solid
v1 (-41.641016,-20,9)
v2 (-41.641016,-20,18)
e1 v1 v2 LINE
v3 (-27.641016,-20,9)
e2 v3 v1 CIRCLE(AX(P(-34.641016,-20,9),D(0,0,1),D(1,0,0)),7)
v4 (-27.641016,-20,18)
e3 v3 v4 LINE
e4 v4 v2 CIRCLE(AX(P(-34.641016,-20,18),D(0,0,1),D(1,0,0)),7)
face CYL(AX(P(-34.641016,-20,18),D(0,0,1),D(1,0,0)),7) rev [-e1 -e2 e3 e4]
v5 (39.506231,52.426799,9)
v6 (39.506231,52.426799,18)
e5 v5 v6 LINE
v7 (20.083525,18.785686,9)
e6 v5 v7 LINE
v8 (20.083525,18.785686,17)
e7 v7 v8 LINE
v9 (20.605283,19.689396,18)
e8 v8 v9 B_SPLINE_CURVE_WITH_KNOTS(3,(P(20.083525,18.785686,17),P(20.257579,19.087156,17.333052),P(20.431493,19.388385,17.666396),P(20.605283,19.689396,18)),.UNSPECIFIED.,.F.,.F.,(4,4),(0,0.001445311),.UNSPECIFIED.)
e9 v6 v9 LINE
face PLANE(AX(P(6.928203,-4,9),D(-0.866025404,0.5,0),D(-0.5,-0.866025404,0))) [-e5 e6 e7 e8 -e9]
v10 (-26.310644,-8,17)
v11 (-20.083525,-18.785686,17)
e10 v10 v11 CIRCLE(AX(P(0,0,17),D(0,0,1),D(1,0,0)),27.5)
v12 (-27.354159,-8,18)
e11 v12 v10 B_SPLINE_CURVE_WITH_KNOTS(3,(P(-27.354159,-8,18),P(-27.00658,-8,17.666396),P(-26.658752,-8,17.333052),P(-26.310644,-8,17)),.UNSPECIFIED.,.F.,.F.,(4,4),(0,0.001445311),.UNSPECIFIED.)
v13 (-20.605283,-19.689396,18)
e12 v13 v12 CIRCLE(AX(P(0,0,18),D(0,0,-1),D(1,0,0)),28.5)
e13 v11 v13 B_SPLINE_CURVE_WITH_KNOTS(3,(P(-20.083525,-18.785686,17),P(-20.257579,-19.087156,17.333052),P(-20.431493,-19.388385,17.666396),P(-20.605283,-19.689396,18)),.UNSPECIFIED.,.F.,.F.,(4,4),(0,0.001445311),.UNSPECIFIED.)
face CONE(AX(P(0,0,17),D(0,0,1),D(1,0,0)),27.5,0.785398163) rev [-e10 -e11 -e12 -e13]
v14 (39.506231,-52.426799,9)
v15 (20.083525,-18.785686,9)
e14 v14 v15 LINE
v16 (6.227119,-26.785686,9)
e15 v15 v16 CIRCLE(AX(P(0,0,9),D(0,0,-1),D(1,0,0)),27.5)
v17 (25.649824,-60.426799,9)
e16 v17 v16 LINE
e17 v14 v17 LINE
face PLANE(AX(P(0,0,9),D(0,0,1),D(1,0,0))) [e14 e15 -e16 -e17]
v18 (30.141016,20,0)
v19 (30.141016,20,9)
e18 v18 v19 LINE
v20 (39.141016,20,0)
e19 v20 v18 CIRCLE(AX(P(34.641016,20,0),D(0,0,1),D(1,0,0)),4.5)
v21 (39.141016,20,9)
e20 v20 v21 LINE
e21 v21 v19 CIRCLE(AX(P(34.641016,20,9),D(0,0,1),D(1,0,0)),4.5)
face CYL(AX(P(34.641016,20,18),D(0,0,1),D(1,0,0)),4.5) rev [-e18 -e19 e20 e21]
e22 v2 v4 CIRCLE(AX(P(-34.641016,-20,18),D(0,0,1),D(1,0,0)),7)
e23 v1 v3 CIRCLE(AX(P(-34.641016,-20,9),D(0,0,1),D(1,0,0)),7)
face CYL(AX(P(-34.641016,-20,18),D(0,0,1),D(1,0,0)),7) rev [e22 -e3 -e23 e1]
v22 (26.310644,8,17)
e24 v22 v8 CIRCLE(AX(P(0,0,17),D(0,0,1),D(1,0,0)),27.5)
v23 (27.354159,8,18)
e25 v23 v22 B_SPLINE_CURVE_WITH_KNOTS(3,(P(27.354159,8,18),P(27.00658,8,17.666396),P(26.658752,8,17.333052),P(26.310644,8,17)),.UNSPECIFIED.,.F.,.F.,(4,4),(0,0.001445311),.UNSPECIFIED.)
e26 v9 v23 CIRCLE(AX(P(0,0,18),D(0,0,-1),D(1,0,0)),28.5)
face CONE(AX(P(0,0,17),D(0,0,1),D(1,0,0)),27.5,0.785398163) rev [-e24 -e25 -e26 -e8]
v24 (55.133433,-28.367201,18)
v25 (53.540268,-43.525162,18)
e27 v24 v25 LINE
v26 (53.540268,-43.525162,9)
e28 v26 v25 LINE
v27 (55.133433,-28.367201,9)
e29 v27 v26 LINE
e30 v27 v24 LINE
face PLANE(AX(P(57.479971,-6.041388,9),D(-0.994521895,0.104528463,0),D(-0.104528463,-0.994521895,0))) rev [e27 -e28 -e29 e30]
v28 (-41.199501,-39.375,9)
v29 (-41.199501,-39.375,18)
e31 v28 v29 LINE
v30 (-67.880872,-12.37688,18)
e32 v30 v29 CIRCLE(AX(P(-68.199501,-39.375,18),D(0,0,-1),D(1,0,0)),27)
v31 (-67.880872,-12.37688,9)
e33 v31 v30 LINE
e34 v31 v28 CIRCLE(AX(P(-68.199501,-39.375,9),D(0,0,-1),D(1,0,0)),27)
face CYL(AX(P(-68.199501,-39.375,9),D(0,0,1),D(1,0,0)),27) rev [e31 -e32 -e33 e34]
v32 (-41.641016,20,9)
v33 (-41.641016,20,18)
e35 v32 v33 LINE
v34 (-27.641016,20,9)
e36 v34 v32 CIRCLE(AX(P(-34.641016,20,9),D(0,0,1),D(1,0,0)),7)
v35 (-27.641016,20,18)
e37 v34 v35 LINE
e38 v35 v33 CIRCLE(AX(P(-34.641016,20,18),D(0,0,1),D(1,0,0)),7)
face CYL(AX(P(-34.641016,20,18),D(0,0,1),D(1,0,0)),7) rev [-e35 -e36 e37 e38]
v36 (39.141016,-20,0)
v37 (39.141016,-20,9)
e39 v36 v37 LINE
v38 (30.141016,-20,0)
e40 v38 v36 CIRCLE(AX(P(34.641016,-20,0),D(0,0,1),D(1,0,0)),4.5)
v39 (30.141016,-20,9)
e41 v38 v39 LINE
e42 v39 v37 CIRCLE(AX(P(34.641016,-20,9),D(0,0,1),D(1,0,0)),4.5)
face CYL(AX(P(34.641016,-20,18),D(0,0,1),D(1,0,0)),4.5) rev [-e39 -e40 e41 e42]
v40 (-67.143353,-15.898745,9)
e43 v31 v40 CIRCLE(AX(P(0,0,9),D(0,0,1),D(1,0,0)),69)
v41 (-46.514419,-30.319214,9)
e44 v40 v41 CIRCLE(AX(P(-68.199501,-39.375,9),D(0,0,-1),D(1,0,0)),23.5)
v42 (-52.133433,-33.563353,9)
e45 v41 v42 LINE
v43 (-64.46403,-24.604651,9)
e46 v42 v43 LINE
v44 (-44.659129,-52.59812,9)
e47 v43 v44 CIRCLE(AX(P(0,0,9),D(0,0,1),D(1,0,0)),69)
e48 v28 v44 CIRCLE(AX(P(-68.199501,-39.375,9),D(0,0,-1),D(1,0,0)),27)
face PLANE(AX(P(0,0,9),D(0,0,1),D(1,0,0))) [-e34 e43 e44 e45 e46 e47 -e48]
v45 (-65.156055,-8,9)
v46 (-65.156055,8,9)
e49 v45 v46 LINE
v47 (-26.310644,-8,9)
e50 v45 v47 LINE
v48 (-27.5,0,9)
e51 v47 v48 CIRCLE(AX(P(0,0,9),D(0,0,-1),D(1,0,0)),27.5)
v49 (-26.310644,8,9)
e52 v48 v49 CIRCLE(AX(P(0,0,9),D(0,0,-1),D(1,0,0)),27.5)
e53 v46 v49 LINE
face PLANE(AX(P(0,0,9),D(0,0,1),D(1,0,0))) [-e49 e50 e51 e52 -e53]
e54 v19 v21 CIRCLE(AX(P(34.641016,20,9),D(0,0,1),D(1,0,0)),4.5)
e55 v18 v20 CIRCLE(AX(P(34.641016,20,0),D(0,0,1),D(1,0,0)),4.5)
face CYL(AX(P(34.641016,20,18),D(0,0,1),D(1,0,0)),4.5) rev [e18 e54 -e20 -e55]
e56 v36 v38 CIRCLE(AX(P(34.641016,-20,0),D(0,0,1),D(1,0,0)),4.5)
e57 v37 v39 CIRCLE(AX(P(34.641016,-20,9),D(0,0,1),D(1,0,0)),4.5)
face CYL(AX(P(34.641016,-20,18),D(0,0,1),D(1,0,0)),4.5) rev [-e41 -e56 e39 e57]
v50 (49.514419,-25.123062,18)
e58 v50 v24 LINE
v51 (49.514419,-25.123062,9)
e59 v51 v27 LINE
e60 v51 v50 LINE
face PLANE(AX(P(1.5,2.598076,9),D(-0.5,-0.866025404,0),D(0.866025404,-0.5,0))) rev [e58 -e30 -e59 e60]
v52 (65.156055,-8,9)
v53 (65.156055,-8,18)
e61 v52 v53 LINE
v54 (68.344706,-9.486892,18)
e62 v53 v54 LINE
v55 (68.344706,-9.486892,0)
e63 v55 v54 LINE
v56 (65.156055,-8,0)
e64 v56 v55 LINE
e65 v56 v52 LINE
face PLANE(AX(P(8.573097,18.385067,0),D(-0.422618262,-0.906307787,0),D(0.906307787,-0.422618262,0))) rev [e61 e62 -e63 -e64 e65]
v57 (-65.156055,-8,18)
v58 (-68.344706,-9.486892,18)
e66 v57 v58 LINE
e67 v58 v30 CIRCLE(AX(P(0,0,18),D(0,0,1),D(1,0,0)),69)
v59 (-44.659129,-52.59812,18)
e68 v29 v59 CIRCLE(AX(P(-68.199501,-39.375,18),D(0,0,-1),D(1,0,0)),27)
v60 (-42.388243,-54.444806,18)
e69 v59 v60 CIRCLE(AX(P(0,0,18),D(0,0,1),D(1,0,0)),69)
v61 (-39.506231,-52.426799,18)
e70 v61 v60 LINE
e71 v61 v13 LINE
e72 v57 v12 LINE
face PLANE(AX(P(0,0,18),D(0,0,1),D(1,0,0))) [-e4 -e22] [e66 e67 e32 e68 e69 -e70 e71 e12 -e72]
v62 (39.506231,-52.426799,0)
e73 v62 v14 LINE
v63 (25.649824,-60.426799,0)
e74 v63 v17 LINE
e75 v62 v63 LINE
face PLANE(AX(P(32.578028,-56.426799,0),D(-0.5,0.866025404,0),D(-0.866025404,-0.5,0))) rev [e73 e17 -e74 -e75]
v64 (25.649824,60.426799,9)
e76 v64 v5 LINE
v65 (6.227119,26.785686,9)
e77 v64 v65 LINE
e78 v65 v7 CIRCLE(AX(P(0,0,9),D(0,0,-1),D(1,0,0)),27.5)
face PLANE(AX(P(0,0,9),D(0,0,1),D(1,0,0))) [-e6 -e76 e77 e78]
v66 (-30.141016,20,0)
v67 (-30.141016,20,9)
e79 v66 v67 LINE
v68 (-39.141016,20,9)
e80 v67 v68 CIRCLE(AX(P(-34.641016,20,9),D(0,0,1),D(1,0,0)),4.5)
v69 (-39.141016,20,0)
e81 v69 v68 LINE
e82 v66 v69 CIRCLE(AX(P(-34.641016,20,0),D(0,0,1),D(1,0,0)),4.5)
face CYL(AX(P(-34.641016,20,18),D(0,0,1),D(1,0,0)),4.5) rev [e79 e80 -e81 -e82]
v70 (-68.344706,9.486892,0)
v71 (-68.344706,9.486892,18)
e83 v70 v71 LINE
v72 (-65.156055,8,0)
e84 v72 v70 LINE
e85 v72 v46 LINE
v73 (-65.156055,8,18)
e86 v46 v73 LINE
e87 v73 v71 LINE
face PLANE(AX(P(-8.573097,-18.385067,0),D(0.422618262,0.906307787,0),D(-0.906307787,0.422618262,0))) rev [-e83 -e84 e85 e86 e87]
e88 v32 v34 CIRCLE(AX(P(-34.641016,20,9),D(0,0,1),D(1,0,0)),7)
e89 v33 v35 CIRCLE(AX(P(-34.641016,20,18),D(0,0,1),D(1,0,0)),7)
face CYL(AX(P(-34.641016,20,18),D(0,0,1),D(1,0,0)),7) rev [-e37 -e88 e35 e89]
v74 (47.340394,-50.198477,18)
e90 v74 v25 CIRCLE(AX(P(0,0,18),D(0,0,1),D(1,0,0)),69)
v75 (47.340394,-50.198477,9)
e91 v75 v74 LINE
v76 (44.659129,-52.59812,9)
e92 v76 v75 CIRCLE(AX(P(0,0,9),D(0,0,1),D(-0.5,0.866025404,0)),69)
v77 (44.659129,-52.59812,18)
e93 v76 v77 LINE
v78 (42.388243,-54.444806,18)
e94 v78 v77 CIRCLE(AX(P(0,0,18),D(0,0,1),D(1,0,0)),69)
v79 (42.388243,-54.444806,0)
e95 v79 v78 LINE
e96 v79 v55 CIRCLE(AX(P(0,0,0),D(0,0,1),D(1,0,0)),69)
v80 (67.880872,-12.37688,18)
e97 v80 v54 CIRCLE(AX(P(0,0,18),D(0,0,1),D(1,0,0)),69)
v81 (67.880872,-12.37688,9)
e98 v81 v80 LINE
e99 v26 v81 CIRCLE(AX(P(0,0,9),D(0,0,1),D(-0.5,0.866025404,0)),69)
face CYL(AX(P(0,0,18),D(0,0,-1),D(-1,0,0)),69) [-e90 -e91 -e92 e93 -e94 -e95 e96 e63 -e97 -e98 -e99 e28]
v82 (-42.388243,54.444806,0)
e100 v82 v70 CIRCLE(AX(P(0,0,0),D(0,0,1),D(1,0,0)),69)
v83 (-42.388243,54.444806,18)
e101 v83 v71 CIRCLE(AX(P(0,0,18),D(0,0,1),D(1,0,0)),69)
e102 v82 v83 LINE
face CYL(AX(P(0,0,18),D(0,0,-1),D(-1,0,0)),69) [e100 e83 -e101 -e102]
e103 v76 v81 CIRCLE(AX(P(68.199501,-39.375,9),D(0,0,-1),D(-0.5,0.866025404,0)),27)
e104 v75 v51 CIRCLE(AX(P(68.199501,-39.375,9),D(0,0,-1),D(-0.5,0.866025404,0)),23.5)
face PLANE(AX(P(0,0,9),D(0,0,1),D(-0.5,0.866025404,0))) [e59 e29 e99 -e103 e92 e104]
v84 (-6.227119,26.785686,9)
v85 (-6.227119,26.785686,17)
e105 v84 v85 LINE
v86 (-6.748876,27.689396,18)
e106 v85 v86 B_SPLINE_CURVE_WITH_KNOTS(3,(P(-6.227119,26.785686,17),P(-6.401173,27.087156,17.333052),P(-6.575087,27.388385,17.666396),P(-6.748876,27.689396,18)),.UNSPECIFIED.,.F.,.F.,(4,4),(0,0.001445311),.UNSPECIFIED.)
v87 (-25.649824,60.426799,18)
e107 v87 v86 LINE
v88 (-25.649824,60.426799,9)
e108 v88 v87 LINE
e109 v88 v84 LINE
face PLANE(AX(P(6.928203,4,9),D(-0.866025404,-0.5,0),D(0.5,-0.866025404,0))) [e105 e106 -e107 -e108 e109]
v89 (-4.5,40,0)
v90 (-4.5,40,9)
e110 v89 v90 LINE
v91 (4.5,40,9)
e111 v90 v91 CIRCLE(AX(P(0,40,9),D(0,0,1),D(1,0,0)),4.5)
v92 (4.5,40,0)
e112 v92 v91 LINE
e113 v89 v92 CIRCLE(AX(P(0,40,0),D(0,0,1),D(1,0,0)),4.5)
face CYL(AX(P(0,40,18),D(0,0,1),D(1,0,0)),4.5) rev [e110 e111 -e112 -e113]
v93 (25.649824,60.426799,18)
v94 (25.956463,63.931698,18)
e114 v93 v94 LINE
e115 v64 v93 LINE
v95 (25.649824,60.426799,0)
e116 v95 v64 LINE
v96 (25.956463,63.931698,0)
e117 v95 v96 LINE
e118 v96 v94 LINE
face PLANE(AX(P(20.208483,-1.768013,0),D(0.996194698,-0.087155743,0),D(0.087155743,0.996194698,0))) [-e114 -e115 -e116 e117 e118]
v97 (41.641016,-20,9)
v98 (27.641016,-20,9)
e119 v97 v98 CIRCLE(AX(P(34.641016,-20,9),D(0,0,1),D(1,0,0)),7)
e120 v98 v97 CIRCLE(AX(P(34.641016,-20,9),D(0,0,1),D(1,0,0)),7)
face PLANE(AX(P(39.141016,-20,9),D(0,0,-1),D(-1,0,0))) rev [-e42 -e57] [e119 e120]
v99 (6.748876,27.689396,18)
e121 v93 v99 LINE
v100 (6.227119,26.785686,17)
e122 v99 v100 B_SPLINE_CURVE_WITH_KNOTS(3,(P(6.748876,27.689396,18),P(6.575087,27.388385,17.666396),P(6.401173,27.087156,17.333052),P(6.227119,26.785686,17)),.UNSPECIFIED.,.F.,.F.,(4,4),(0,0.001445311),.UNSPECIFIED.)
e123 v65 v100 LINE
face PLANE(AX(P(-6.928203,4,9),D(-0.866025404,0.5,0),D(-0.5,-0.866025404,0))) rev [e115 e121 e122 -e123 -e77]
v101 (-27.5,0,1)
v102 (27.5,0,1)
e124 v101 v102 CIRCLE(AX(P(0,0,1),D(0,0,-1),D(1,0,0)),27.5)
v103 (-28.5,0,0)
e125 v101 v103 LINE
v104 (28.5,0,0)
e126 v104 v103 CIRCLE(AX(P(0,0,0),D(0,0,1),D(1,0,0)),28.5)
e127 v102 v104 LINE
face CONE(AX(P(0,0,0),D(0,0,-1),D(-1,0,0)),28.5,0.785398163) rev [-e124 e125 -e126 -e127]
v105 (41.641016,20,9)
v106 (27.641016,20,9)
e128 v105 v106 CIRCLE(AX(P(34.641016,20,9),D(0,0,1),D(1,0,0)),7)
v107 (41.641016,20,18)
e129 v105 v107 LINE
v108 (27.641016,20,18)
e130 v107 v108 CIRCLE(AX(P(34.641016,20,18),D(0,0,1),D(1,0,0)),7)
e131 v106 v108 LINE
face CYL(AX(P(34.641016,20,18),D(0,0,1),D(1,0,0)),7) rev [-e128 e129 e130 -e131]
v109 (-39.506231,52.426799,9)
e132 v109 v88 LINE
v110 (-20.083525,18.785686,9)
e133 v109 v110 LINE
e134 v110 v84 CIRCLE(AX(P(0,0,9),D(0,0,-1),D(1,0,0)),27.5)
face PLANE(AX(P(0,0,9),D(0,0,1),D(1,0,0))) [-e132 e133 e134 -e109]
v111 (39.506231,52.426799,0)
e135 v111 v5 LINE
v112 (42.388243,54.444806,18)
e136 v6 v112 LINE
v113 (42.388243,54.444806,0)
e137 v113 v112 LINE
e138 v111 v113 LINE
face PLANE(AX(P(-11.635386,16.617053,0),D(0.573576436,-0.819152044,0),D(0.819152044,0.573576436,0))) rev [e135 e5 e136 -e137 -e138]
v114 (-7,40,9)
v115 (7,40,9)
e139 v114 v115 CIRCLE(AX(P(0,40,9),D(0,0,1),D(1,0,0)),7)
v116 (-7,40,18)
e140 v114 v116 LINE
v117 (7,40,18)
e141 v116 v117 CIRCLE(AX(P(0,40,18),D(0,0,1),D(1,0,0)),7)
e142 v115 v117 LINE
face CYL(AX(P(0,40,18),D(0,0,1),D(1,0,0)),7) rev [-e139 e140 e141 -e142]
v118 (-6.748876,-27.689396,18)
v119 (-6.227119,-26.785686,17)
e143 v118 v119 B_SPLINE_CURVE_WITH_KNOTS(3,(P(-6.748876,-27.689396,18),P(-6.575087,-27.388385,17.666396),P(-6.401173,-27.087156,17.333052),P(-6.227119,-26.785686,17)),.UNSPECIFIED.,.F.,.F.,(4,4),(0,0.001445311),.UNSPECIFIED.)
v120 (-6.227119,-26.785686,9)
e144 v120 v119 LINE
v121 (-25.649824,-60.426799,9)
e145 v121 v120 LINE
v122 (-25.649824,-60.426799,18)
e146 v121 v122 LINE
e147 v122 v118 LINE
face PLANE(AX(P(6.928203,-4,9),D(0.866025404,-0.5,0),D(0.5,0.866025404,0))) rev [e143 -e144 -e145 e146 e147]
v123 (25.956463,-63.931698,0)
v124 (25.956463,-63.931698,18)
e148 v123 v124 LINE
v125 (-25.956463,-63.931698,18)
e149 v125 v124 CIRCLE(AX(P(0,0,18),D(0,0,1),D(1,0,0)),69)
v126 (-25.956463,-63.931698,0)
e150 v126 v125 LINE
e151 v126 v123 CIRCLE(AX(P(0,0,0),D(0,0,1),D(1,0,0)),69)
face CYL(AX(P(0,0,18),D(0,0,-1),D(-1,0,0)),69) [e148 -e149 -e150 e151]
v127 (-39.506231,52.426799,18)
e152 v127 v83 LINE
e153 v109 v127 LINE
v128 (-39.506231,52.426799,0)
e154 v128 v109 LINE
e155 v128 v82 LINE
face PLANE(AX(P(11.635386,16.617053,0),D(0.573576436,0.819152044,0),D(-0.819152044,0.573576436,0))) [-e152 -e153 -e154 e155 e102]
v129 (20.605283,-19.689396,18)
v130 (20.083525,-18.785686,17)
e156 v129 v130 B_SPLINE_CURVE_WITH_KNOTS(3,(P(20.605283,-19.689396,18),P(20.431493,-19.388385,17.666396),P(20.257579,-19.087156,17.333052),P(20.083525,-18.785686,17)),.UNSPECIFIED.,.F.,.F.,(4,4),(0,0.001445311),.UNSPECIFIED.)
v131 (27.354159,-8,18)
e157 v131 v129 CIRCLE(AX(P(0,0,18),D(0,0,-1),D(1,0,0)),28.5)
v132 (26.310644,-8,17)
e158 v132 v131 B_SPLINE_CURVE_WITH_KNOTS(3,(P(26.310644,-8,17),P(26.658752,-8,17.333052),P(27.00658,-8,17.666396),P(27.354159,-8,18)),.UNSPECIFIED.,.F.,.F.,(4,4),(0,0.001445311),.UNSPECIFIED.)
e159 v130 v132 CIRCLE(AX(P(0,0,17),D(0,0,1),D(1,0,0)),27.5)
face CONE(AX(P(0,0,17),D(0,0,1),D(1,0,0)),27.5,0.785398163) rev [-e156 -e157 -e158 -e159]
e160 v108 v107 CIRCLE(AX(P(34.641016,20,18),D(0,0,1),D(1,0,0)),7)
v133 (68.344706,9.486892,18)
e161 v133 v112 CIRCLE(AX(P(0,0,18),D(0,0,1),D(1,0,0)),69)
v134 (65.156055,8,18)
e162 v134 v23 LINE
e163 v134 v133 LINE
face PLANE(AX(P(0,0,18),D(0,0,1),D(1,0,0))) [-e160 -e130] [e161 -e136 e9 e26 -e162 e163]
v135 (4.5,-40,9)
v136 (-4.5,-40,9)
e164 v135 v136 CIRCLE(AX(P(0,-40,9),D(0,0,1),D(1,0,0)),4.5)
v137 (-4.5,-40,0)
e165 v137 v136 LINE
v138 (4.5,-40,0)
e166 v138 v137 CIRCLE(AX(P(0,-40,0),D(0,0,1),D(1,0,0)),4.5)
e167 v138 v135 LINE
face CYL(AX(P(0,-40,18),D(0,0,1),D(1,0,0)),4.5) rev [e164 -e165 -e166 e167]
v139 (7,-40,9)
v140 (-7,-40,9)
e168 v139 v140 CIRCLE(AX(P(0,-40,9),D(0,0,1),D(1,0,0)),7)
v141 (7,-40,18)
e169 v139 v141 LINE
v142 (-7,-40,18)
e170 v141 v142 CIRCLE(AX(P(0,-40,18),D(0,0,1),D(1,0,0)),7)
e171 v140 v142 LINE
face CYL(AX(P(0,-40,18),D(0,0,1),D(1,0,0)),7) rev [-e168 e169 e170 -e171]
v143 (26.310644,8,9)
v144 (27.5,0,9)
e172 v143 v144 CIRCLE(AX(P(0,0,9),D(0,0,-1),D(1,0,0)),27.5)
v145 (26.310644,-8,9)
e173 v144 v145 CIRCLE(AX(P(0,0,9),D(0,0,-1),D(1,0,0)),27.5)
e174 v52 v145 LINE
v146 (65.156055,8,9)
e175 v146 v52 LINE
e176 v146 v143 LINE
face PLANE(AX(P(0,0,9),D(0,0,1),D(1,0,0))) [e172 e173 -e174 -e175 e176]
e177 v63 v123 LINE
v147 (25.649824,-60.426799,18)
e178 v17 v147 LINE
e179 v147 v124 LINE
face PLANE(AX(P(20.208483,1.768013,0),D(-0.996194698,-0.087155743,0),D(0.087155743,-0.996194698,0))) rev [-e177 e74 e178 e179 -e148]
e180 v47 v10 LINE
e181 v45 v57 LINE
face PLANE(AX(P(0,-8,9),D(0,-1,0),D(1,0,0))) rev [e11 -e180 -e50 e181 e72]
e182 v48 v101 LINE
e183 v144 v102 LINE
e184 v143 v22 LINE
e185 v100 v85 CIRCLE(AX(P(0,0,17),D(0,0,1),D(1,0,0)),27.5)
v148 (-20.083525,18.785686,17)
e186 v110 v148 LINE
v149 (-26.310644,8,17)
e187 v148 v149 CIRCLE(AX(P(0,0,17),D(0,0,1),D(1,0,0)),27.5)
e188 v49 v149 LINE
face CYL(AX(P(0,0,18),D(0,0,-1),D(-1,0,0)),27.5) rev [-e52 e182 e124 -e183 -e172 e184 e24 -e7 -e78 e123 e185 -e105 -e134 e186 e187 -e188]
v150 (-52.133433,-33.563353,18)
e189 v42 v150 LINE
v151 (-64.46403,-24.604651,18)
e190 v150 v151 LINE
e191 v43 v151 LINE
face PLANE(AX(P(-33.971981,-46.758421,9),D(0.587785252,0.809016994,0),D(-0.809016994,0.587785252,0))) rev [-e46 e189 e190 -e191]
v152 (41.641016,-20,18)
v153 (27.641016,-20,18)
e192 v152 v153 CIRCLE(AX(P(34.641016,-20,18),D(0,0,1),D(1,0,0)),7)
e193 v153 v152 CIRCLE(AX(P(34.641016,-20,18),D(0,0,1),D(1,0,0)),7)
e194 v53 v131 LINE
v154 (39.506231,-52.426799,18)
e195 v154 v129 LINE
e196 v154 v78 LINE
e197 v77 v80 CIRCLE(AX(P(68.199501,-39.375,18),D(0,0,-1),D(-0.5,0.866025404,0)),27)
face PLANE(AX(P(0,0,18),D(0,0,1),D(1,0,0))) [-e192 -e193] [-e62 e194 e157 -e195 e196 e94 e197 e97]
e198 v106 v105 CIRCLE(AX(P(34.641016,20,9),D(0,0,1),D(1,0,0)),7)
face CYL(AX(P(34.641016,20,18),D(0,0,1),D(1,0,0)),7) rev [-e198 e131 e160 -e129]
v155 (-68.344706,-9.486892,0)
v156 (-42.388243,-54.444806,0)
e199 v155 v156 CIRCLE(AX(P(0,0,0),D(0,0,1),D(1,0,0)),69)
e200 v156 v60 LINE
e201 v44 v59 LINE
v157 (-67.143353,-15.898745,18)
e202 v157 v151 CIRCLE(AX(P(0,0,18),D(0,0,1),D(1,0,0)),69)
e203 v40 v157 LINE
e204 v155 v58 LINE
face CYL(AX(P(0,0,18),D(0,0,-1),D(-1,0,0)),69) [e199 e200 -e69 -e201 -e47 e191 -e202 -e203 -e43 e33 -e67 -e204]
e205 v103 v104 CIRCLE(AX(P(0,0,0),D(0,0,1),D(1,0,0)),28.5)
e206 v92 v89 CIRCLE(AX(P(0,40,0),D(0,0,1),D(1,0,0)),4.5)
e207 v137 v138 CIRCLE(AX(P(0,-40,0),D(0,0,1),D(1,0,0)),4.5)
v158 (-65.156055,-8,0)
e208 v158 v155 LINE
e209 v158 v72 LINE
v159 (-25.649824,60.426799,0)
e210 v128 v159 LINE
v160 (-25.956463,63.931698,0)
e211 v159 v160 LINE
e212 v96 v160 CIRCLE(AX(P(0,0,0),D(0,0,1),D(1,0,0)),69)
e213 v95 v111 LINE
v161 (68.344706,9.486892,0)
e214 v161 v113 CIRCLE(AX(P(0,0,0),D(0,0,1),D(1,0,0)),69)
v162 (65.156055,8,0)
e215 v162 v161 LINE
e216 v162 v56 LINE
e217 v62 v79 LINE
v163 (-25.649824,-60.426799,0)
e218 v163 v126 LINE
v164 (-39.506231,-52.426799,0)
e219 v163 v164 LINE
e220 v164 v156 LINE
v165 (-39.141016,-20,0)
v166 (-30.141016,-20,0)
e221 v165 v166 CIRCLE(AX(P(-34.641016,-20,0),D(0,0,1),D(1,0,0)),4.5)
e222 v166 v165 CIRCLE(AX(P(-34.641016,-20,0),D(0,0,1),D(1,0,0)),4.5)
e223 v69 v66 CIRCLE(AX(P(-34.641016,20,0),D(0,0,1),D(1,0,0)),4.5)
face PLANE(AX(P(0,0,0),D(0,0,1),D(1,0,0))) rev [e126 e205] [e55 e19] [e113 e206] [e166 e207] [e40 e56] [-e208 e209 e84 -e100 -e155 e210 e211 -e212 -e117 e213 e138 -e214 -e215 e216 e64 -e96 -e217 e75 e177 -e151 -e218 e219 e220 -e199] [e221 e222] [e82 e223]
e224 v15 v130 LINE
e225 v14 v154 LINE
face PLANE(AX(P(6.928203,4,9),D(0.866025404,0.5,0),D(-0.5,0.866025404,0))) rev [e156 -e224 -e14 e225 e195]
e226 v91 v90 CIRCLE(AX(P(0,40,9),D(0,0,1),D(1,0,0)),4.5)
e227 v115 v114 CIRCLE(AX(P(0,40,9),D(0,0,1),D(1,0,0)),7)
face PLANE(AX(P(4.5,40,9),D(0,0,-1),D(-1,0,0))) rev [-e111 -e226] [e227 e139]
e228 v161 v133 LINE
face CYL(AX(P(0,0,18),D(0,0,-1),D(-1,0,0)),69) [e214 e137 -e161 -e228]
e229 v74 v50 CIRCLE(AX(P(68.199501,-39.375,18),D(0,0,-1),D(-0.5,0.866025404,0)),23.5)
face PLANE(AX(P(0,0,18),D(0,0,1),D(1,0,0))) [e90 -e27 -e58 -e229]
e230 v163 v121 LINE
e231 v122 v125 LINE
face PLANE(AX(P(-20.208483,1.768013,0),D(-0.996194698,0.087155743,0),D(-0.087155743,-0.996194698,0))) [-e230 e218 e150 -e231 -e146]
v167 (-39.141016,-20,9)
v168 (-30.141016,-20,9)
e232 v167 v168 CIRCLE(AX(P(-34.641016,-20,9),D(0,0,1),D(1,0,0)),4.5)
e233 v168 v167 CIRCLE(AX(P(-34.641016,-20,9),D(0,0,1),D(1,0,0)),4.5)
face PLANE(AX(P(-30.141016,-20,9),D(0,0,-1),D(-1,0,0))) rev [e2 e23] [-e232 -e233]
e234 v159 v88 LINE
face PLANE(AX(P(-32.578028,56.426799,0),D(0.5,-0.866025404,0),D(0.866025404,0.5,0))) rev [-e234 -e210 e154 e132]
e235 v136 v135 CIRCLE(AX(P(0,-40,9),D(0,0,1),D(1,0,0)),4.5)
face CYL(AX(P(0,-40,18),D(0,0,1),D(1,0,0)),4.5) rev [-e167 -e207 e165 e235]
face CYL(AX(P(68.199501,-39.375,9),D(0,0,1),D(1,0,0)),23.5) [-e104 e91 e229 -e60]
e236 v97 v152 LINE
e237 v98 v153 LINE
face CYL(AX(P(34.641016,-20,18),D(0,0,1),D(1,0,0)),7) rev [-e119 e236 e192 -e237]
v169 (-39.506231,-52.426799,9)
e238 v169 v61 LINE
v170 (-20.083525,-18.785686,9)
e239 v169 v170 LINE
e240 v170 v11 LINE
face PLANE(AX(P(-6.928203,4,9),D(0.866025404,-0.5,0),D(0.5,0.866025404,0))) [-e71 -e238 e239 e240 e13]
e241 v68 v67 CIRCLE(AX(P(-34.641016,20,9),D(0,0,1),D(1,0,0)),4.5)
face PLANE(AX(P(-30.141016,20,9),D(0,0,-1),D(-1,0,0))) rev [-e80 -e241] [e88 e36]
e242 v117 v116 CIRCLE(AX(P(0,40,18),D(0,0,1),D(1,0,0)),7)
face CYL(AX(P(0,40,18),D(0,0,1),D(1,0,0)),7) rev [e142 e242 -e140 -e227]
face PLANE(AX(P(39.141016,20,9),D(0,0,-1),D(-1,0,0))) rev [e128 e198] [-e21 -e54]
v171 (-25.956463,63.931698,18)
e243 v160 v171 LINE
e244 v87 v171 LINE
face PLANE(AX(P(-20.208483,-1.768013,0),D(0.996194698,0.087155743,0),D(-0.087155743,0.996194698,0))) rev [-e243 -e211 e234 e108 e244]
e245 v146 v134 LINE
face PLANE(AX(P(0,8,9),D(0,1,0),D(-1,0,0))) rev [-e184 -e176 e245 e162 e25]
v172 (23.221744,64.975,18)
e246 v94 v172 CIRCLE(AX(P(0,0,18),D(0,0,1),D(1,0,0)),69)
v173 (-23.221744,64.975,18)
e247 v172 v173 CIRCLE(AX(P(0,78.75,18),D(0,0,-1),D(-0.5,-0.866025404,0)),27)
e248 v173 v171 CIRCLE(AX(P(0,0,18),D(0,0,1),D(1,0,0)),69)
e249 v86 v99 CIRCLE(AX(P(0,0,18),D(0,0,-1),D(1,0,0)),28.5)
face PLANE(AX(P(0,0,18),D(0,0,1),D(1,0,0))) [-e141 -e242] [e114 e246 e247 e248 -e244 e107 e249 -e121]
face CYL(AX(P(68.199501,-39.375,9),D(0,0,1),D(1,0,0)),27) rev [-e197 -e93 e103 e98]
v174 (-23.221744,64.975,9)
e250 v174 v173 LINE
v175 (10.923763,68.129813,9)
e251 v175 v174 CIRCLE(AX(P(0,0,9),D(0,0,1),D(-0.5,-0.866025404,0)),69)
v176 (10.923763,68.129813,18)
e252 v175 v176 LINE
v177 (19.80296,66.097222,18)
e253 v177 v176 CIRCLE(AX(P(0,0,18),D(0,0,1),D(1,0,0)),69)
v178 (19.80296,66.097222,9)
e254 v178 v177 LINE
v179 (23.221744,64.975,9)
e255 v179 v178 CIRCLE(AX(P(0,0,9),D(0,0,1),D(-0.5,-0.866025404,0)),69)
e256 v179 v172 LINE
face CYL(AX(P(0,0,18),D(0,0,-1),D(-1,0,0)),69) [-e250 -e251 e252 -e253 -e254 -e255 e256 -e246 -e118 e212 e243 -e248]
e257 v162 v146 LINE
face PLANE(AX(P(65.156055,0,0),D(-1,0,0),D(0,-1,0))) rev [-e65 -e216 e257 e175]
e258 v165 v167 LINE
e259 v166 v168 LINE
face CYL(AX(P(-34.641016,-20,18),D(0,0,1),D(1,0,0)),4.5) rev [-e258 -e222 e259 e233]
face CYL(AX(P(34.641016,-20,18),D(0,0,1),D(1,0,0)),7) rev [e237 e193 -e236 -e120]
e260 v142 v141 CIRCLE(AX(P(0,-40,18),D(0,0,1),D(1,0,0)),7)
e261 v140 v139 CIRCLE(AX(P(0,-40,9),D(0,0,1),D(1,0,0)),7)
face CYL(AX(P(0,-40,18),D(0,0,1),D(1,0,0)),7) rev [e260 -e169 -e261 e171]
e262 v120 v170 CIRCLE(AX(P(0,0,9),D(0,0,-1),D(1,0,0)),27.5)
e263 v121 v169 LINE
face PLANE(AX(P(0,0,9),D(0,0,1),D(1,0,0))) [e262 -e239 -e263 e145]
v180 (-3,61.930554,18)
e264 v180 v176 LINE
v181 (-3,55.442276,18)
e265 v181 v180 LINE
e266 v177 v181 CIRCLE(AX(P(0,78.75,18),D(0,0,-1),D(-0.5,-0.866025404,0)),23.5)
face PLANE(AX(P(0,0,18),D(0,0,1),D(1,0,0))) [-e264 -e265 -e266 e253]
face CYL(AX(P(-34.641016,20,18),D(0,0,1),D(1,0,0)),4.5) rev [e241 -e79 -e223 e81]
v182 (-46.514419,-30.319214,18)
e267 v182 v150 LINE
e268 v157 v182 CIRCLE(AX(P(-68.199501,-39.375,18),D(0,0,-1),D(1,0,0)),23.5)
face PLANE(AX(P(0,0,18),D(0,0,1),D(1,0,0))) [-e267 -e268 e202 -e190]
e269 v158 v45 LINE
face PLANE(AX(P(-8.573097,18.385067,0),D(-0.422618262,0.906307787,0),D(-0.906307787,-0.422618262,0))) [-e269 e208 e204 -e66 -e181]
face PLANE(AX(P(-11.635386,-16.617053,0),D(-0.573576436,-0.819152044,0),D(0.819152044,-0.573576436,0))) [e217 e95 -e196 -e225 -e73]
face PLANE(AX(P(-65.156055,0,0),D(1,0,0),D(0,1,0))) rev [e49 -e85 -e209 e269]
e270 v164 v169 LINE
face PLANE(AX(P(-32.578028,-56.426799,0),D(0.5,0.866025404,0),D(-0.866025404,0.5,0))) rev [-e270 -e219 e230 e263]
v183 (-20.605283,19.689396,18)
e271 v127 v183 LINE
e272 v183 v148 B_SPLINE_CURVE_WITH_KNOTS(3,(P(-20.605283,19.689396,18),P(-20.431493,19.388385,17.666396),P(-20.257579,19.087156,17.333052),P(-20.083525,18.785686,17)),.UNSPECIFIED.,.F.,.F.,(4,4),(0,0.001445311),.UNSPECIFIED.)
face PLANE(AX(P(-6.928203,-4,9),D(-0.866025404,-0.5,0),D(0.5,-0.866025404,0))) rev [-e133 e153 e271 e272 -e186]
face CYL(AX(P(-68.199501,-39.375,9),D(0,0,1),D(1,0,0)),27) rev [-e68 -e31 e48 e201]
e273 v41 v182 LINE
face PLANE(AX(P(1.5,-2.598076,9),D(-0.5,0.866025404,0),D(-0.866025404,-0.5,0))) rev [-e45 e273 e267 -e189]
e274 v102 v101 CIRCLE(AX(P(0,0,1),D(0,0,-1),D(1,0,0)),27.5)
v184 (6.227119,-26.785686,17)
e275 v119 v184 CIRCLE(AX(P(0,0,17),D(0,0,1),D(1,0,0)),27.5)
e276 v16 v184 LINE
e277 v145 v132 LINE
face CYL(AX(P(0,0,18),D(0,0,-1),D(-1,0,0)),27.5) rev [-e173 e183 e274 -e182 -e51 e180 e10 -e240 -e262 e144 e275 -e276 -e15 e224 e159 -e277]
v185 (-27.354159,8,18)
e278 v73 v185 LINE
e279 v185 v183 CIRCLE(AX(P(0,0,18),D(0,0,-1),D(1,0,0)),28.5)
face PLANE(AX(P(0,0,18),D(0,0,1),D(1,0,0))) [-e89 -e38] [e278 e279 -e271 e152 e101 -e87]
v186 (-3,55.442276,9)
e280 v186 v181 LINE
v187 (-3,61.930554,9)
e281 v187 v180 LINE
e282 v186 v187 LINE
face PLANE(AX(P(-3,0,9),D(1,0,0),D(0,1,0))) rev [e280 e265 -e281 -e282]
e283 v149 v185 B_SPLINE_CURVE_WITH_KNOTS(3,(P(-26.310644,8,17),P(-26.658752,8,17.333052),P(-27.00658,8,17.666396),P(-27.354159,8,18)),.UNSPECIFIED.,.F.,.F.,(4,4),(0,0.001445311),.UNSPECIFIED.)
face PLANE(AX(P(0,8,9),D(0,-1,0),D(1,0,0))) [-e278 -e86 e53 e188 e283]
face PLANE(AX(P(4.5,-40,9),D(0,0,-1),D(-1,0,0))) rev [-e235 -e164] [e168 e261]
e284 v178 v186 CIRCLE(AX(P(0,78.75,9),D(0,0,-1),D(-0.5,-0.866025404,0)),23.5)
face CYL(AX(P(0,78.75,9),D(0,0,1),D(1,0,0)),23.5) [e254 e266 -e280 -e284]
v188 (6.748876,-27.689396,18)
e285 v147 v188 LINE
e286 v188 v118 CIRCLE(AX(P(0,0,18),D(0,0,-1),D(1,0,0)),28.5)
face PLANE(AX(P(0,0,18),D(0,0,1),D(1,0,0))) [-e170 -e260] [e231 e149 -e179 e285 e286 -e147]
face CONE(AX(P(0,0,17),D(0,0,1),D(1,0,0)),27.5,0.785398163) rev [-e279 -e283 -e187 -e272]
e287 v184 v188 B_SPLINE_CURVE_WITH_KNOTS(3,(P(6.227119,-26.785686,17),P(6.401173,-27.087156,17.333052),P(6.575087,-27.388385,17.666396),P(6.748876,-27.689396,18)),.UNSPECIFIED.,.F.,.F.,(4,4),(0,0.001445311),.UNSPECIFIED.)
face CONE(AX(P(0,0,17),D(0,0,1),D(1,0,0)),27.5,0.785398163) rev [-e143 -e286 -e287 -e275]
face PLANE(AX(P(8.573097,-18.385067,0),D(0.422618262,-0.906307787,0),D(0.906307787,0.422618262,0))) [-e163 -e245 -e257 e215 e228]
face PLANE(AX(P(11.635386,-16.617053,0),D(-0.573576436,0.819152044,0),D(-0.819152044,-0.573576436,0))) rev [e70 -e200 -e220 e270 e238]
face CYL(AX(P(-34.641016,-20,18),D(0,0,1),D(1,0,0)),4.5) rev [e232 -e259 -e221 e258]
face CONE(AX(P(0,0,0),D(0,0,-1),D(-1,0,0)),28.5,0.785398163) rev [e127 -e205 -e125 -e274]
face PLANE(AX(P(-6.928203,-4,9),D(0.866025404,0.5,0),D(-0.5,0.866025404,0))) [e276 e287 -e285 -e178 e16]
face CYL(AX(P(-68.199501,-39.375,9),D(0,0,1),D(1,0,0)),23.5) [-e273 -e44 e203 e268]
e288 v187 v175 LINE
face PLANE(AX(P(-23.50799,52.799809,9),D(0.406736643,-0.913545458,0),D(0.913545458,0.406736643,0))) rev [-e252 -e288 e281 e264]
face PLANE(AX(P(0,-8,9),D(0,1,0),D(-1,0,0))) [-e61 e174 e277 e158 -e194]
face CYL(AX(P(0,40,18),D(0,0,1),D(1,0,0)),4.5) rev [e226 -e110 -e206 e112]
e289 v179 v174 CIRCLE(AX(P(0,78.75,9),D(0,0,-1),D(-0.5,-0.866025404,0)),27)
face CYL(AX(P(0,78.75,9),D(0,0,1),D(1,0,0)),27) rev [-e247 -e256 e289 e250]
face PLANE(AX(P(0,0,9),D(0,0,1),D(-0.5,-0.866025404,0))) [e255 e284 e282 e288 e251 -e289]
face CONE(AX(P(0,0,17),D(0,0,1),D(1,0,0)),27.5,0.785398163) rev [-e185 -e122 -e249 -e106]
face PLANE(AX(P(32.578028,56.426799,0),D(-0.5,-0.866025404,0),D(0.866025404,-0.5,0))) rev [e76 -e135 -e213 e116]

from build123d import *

# Parameters (mm, degrees)
FLANGE_DISC_SKETCH_R                = 69
FLANGE_DISC_SKETCH_R_2              = 27.5
FLANGE_DISC_138_X_18_DEPTH          = 18
JAW_START                           = -9
JAW_RECESSES_9_DEEP_DEPTH           = 9
PORT_PROFILE_CUT_DEPTH              = 100.227012451
COUNTERBORED_HOLES_6X_9_D           = 9
COUNTERBORED_HOLES_6X_9_CBORE_D     = 14
COUNTERBORED_HOLES_6X_9_CBORE_DEPTH = 9
HOOK_START                          = -9
HOOK_SLOT_9_DEEP_DEPTH              = 9
HOOK_SLOT_PATTERN_3X_COUNT          = 3
EDGE_CHAMFER_1X45_SIZE              = 1


with BuildPart() as part:
    # Flange Disc Sketch → Flange Disc _138 x 18 (new body)
    with BuildSketch(Plane.XY):
        Circle(FLANGE_DISC_SKETCH_R)
        Circle(FLANGE_DISC_SKETCH_R_2, mode=Mode.SUBTRACT)
    extrude(amount=FLANGE_DISC_138_X_18_DEPTH)

    # Jaw And Port Sketch → Jaw Recesses 9 Deep (cut)
    with BuildSketch(Plane.XY.offset(18).offset(JAW_START)):
        with BuildLine():
            ThreePointArc((-26.310644234, -8), (-27.5, 0), (-26.310644234, 8))
            Line((-26.310644234, 8), (-65.156055364, 8))
            Line((-65.156055364, 8), (-65.156055364, -8))
            Line((-65.156055364, -8), (-26.310644234, -8))
        make_face()
        with BuildLine():
            Line((-6.227118887, 26.785686296), (-25.649824452, 60.426799156))
            Line((-25.649824452, 60.426799156), (-39.506230912, 52.426799156))
            Line((-39.506230912, 52.426799156), (-20.083525347, 18.785686296))
            ThreePointArc((-20.083525347, 18.785686296), (-13.75, 23.815698604), (-6.227118887, 26.785686296))
        make_face()
        with BuildLine():
            Line((25.649824452, 60.426799156), (6.227118887, 26.785686296))
            ThreePointArc((6.227118887, 26.785686296), (13.75, 23.815698604), (20.083525347, 18.785686296))
            Line((20.083525347, 18.785686296), (39.506230912, 52.426799156))
            Line((39.506230912, 52.426799156), (25.649824452, 60.426799156))
        make_face()
        with BuildLine():
            Line((65.156055364, 8), (26.310644234, 8))
            ThreePointArc((26.310644234, 8), (27.201035977, 4.043963623), (27.5, 0))
            ThreePointArc((27.5, 0), (27.201035977, -4.043963623), (26.310644234, -8))
            Line((26.310644234, -8), (65.156055364, -8))
            Line((65.156055364, -8), (65.156055364, 8))
        make_face()
        with BuildLine():
            Line((39.506230912, -52.426799156), (20.083525347, -18.785686296))
            ThreePointArc((20.083525347, -18.785686296), (13.75, -23.815698604), (6.227118887, -26.785686296))
            Line((6.227118887, -26.785686296), (25.649824452, -60.426799156))
            Line((25.649824452, -60.426799156), (39.506230912, -52.426799156))
        make_face()
        with BuildLine():
            ThreePointArc((-6.227118887, -26.785686296), (-13.75, -23.815698604), (-20.083525347, -18.785686296))
            Line((-20.083525347, -18.785686296), (-39.506230912, -52.426799156))
            Line((-39.506230912, -52.426799156), (-25.649824452, -60.426799156))
            Line((-25.649824452, -60.426799156), (-6.227118887, -26.785686296))
        make_face()
    extrude(amount=JAW_RECESSES_9_DEEP_DEPTH, mode=Mode.SUBTRACT)

    # Sketch3_3 → Port Profile Cut (cut, through all)
    with BuildSketch(Plane.XY.offset(18)):
        with BuildLine():
            Line((-65.156055364, 8), (-68.344706261, 9.486892332))
            ThreePointArc((-68.344706261, 9.486892332), (-69, 0), (-68.344706261, -9.486892332))
            Line((-68.344706261, -9.486892332), (-65.156055364, -8))
            Line((-65.156055364, -8), (-65.156055364, 8))
        make_face()
        with BuildLine():
            Line((-39.506230912, -52.426799156), (-42.388242893, -54.44480567))
            ThreePointArc((-42.388242893, -54.44480567), (-34.5, -59.755752861), (-25.956463368, -63.931698002))
            Line((-25.956463368, -63.931698002), (-25.649824452, -60.426799156))
            Line((-25.649824452, -60.426799156), (-39.506230912, -52.426799156))
        make_face()
        with BuildLine():
            ThreePointArc((25.956463368, -63.931698002), (34.5, -59.755752861), (42.388242893, -54.44480567))
            Line((42.388242893, -54.44480567), (39.506230912, -52.426799156))
            Line((39.506230912, -52.426799156), (25.649824452, -60.426799156))
            Line((25.649824452, -60.426799156), (25.956463368, -63.931698002))
        make_face()
        with BuildLine():
            ThreePointArc((69, 0), (68.835981623, 4.754748574), (68.344706261, 9.486892332))
            Line((68.344706261, 9.486892332), (65.156055364, 8))
            Line((65.156055364, 8), (65.156055364, -8))
            Line((65.156055364, -8), (68.344706261, -9.486892332))
            ThreePointArc((68.344706261, -9.486892332), (68.835981623, -4.754748574), (69, 0))
        make_face()
        with BuildLine():
            ThreePointArc((42.388242893, 54.44480567), (34.5, 59.755752861), (25.956463368, 63.931698002))
            Line((25.956463368, 63.931698002), (25.649824452, 60.426799156))
            Line((25.649824452, 60.426799156), (39.506230912, 52.426799156))
            Line((39.506230912, 52.426799156), (42.388242893, 54.44480567))
        make_face()
        with BuildLine():
            Line((-39.506230912, 52.426799156), (-25.649824452, 60.426799156))
            Line((-25.649824452, 60.426799156), (-25.956463368, 63.931698002))
            ThreePointArc((-25.956463368, 63.931698002), (-34.5, 59.755752861), (-42.388242893, 54.44480567))
            Line((-42.388242893, 54.44480567), (-39.506230912, 52.426799156))
        make_face()
    extrude(amount=-PORT_PROFILE_CUT_DEPTH, mode=Mode.SUBTRACT)

    # Counterbored Holes 6x_9 (through all)
    with Locations(Plane.XY.offset(18)):
        with Locations((0, 40), (34.641016151, 20), (34.641016151, -20), (0, -40), (-34.641016151, -20), (-34.641016151, 20)):
            CounterBoreHole(COUNTERBORED_HOLES_6X_9_D / 2, COUNTERBORED_HOLES_6X_9_CBORE_D / 2, COUNTERBORED_HOLES_6X_9_CBORE_DEPTH)

    # Hook Slot Sketch → Hook Slot 9 Deep (cut)
    with BuildSketch(Plane.XY.offset(18).offset(HOOK_START)):
        with BuildLine():
            ThreePointArc((-67.143353435, -15.898744905), (-54.735535714, -20.114375634), (-46.514419424, -30.319214191))
            Line((-46.514419424, -30.319214191), (-52.133433448, -33.56335345))
            Line((-52.133433448, -33.56335345), (-64.464030022, -24.604650643))
            ThreePointArc((-64.464030022, -24.604650643), (-56.328274682, -39.851291966), (-44.65912882, -52.598119862))
            ThreePointArc((-44.65912882, -52.598119862), (-44.816814646, -25.875), (-67.880872402, -12.376880138))
            ThreePointArc((-67.880872402, -12.376880138), (-67.535074395, -14.142620919), (-67.143353435, -15.898744905))
        make_face()
    hook_slot_9_deep = extrude(amount=HOOK_SLOT_9_DEEP_DEPTH, mode=Mode.SUBTRACT)

    # Hook Slot Pattern 3x: Hook Slot 9 Deep ×3 about axis
    hook_slot_pattern_3x_axis = Axis((0, 0, 0), (0, 0, 1))
    for i in range(1, HOOK_SLOT_PATTERN_3X_COUNT):
        add(hook_slot_9_deep.rotate(hook_slot_pattern_3x_axis, i * 360 / HOOK_SLOT_PATTERN_3X_COUNT), mode=Mode.SUBTRACT)

    # Edge Chamfer 1x45
    edge_chamfer_1x45_edges = [part.edges().sort_by_distance(p)[0] for p in [
        (0, 27.5, 18),
        (-23.815698604, 13.75, 18),
        (-23.815698604, -13.75, 18),
        (0, -27.5, 18),
        (23.815698604, -13.75, 18),
        (-27.5, 0, 0),
        (23.815698604, 13.75, 18),
    ]]
    chamfer(edge_chamfer_1x45_edges, length=EDGE_CHAMFER_1X45_SIZE)


solid = part.part
